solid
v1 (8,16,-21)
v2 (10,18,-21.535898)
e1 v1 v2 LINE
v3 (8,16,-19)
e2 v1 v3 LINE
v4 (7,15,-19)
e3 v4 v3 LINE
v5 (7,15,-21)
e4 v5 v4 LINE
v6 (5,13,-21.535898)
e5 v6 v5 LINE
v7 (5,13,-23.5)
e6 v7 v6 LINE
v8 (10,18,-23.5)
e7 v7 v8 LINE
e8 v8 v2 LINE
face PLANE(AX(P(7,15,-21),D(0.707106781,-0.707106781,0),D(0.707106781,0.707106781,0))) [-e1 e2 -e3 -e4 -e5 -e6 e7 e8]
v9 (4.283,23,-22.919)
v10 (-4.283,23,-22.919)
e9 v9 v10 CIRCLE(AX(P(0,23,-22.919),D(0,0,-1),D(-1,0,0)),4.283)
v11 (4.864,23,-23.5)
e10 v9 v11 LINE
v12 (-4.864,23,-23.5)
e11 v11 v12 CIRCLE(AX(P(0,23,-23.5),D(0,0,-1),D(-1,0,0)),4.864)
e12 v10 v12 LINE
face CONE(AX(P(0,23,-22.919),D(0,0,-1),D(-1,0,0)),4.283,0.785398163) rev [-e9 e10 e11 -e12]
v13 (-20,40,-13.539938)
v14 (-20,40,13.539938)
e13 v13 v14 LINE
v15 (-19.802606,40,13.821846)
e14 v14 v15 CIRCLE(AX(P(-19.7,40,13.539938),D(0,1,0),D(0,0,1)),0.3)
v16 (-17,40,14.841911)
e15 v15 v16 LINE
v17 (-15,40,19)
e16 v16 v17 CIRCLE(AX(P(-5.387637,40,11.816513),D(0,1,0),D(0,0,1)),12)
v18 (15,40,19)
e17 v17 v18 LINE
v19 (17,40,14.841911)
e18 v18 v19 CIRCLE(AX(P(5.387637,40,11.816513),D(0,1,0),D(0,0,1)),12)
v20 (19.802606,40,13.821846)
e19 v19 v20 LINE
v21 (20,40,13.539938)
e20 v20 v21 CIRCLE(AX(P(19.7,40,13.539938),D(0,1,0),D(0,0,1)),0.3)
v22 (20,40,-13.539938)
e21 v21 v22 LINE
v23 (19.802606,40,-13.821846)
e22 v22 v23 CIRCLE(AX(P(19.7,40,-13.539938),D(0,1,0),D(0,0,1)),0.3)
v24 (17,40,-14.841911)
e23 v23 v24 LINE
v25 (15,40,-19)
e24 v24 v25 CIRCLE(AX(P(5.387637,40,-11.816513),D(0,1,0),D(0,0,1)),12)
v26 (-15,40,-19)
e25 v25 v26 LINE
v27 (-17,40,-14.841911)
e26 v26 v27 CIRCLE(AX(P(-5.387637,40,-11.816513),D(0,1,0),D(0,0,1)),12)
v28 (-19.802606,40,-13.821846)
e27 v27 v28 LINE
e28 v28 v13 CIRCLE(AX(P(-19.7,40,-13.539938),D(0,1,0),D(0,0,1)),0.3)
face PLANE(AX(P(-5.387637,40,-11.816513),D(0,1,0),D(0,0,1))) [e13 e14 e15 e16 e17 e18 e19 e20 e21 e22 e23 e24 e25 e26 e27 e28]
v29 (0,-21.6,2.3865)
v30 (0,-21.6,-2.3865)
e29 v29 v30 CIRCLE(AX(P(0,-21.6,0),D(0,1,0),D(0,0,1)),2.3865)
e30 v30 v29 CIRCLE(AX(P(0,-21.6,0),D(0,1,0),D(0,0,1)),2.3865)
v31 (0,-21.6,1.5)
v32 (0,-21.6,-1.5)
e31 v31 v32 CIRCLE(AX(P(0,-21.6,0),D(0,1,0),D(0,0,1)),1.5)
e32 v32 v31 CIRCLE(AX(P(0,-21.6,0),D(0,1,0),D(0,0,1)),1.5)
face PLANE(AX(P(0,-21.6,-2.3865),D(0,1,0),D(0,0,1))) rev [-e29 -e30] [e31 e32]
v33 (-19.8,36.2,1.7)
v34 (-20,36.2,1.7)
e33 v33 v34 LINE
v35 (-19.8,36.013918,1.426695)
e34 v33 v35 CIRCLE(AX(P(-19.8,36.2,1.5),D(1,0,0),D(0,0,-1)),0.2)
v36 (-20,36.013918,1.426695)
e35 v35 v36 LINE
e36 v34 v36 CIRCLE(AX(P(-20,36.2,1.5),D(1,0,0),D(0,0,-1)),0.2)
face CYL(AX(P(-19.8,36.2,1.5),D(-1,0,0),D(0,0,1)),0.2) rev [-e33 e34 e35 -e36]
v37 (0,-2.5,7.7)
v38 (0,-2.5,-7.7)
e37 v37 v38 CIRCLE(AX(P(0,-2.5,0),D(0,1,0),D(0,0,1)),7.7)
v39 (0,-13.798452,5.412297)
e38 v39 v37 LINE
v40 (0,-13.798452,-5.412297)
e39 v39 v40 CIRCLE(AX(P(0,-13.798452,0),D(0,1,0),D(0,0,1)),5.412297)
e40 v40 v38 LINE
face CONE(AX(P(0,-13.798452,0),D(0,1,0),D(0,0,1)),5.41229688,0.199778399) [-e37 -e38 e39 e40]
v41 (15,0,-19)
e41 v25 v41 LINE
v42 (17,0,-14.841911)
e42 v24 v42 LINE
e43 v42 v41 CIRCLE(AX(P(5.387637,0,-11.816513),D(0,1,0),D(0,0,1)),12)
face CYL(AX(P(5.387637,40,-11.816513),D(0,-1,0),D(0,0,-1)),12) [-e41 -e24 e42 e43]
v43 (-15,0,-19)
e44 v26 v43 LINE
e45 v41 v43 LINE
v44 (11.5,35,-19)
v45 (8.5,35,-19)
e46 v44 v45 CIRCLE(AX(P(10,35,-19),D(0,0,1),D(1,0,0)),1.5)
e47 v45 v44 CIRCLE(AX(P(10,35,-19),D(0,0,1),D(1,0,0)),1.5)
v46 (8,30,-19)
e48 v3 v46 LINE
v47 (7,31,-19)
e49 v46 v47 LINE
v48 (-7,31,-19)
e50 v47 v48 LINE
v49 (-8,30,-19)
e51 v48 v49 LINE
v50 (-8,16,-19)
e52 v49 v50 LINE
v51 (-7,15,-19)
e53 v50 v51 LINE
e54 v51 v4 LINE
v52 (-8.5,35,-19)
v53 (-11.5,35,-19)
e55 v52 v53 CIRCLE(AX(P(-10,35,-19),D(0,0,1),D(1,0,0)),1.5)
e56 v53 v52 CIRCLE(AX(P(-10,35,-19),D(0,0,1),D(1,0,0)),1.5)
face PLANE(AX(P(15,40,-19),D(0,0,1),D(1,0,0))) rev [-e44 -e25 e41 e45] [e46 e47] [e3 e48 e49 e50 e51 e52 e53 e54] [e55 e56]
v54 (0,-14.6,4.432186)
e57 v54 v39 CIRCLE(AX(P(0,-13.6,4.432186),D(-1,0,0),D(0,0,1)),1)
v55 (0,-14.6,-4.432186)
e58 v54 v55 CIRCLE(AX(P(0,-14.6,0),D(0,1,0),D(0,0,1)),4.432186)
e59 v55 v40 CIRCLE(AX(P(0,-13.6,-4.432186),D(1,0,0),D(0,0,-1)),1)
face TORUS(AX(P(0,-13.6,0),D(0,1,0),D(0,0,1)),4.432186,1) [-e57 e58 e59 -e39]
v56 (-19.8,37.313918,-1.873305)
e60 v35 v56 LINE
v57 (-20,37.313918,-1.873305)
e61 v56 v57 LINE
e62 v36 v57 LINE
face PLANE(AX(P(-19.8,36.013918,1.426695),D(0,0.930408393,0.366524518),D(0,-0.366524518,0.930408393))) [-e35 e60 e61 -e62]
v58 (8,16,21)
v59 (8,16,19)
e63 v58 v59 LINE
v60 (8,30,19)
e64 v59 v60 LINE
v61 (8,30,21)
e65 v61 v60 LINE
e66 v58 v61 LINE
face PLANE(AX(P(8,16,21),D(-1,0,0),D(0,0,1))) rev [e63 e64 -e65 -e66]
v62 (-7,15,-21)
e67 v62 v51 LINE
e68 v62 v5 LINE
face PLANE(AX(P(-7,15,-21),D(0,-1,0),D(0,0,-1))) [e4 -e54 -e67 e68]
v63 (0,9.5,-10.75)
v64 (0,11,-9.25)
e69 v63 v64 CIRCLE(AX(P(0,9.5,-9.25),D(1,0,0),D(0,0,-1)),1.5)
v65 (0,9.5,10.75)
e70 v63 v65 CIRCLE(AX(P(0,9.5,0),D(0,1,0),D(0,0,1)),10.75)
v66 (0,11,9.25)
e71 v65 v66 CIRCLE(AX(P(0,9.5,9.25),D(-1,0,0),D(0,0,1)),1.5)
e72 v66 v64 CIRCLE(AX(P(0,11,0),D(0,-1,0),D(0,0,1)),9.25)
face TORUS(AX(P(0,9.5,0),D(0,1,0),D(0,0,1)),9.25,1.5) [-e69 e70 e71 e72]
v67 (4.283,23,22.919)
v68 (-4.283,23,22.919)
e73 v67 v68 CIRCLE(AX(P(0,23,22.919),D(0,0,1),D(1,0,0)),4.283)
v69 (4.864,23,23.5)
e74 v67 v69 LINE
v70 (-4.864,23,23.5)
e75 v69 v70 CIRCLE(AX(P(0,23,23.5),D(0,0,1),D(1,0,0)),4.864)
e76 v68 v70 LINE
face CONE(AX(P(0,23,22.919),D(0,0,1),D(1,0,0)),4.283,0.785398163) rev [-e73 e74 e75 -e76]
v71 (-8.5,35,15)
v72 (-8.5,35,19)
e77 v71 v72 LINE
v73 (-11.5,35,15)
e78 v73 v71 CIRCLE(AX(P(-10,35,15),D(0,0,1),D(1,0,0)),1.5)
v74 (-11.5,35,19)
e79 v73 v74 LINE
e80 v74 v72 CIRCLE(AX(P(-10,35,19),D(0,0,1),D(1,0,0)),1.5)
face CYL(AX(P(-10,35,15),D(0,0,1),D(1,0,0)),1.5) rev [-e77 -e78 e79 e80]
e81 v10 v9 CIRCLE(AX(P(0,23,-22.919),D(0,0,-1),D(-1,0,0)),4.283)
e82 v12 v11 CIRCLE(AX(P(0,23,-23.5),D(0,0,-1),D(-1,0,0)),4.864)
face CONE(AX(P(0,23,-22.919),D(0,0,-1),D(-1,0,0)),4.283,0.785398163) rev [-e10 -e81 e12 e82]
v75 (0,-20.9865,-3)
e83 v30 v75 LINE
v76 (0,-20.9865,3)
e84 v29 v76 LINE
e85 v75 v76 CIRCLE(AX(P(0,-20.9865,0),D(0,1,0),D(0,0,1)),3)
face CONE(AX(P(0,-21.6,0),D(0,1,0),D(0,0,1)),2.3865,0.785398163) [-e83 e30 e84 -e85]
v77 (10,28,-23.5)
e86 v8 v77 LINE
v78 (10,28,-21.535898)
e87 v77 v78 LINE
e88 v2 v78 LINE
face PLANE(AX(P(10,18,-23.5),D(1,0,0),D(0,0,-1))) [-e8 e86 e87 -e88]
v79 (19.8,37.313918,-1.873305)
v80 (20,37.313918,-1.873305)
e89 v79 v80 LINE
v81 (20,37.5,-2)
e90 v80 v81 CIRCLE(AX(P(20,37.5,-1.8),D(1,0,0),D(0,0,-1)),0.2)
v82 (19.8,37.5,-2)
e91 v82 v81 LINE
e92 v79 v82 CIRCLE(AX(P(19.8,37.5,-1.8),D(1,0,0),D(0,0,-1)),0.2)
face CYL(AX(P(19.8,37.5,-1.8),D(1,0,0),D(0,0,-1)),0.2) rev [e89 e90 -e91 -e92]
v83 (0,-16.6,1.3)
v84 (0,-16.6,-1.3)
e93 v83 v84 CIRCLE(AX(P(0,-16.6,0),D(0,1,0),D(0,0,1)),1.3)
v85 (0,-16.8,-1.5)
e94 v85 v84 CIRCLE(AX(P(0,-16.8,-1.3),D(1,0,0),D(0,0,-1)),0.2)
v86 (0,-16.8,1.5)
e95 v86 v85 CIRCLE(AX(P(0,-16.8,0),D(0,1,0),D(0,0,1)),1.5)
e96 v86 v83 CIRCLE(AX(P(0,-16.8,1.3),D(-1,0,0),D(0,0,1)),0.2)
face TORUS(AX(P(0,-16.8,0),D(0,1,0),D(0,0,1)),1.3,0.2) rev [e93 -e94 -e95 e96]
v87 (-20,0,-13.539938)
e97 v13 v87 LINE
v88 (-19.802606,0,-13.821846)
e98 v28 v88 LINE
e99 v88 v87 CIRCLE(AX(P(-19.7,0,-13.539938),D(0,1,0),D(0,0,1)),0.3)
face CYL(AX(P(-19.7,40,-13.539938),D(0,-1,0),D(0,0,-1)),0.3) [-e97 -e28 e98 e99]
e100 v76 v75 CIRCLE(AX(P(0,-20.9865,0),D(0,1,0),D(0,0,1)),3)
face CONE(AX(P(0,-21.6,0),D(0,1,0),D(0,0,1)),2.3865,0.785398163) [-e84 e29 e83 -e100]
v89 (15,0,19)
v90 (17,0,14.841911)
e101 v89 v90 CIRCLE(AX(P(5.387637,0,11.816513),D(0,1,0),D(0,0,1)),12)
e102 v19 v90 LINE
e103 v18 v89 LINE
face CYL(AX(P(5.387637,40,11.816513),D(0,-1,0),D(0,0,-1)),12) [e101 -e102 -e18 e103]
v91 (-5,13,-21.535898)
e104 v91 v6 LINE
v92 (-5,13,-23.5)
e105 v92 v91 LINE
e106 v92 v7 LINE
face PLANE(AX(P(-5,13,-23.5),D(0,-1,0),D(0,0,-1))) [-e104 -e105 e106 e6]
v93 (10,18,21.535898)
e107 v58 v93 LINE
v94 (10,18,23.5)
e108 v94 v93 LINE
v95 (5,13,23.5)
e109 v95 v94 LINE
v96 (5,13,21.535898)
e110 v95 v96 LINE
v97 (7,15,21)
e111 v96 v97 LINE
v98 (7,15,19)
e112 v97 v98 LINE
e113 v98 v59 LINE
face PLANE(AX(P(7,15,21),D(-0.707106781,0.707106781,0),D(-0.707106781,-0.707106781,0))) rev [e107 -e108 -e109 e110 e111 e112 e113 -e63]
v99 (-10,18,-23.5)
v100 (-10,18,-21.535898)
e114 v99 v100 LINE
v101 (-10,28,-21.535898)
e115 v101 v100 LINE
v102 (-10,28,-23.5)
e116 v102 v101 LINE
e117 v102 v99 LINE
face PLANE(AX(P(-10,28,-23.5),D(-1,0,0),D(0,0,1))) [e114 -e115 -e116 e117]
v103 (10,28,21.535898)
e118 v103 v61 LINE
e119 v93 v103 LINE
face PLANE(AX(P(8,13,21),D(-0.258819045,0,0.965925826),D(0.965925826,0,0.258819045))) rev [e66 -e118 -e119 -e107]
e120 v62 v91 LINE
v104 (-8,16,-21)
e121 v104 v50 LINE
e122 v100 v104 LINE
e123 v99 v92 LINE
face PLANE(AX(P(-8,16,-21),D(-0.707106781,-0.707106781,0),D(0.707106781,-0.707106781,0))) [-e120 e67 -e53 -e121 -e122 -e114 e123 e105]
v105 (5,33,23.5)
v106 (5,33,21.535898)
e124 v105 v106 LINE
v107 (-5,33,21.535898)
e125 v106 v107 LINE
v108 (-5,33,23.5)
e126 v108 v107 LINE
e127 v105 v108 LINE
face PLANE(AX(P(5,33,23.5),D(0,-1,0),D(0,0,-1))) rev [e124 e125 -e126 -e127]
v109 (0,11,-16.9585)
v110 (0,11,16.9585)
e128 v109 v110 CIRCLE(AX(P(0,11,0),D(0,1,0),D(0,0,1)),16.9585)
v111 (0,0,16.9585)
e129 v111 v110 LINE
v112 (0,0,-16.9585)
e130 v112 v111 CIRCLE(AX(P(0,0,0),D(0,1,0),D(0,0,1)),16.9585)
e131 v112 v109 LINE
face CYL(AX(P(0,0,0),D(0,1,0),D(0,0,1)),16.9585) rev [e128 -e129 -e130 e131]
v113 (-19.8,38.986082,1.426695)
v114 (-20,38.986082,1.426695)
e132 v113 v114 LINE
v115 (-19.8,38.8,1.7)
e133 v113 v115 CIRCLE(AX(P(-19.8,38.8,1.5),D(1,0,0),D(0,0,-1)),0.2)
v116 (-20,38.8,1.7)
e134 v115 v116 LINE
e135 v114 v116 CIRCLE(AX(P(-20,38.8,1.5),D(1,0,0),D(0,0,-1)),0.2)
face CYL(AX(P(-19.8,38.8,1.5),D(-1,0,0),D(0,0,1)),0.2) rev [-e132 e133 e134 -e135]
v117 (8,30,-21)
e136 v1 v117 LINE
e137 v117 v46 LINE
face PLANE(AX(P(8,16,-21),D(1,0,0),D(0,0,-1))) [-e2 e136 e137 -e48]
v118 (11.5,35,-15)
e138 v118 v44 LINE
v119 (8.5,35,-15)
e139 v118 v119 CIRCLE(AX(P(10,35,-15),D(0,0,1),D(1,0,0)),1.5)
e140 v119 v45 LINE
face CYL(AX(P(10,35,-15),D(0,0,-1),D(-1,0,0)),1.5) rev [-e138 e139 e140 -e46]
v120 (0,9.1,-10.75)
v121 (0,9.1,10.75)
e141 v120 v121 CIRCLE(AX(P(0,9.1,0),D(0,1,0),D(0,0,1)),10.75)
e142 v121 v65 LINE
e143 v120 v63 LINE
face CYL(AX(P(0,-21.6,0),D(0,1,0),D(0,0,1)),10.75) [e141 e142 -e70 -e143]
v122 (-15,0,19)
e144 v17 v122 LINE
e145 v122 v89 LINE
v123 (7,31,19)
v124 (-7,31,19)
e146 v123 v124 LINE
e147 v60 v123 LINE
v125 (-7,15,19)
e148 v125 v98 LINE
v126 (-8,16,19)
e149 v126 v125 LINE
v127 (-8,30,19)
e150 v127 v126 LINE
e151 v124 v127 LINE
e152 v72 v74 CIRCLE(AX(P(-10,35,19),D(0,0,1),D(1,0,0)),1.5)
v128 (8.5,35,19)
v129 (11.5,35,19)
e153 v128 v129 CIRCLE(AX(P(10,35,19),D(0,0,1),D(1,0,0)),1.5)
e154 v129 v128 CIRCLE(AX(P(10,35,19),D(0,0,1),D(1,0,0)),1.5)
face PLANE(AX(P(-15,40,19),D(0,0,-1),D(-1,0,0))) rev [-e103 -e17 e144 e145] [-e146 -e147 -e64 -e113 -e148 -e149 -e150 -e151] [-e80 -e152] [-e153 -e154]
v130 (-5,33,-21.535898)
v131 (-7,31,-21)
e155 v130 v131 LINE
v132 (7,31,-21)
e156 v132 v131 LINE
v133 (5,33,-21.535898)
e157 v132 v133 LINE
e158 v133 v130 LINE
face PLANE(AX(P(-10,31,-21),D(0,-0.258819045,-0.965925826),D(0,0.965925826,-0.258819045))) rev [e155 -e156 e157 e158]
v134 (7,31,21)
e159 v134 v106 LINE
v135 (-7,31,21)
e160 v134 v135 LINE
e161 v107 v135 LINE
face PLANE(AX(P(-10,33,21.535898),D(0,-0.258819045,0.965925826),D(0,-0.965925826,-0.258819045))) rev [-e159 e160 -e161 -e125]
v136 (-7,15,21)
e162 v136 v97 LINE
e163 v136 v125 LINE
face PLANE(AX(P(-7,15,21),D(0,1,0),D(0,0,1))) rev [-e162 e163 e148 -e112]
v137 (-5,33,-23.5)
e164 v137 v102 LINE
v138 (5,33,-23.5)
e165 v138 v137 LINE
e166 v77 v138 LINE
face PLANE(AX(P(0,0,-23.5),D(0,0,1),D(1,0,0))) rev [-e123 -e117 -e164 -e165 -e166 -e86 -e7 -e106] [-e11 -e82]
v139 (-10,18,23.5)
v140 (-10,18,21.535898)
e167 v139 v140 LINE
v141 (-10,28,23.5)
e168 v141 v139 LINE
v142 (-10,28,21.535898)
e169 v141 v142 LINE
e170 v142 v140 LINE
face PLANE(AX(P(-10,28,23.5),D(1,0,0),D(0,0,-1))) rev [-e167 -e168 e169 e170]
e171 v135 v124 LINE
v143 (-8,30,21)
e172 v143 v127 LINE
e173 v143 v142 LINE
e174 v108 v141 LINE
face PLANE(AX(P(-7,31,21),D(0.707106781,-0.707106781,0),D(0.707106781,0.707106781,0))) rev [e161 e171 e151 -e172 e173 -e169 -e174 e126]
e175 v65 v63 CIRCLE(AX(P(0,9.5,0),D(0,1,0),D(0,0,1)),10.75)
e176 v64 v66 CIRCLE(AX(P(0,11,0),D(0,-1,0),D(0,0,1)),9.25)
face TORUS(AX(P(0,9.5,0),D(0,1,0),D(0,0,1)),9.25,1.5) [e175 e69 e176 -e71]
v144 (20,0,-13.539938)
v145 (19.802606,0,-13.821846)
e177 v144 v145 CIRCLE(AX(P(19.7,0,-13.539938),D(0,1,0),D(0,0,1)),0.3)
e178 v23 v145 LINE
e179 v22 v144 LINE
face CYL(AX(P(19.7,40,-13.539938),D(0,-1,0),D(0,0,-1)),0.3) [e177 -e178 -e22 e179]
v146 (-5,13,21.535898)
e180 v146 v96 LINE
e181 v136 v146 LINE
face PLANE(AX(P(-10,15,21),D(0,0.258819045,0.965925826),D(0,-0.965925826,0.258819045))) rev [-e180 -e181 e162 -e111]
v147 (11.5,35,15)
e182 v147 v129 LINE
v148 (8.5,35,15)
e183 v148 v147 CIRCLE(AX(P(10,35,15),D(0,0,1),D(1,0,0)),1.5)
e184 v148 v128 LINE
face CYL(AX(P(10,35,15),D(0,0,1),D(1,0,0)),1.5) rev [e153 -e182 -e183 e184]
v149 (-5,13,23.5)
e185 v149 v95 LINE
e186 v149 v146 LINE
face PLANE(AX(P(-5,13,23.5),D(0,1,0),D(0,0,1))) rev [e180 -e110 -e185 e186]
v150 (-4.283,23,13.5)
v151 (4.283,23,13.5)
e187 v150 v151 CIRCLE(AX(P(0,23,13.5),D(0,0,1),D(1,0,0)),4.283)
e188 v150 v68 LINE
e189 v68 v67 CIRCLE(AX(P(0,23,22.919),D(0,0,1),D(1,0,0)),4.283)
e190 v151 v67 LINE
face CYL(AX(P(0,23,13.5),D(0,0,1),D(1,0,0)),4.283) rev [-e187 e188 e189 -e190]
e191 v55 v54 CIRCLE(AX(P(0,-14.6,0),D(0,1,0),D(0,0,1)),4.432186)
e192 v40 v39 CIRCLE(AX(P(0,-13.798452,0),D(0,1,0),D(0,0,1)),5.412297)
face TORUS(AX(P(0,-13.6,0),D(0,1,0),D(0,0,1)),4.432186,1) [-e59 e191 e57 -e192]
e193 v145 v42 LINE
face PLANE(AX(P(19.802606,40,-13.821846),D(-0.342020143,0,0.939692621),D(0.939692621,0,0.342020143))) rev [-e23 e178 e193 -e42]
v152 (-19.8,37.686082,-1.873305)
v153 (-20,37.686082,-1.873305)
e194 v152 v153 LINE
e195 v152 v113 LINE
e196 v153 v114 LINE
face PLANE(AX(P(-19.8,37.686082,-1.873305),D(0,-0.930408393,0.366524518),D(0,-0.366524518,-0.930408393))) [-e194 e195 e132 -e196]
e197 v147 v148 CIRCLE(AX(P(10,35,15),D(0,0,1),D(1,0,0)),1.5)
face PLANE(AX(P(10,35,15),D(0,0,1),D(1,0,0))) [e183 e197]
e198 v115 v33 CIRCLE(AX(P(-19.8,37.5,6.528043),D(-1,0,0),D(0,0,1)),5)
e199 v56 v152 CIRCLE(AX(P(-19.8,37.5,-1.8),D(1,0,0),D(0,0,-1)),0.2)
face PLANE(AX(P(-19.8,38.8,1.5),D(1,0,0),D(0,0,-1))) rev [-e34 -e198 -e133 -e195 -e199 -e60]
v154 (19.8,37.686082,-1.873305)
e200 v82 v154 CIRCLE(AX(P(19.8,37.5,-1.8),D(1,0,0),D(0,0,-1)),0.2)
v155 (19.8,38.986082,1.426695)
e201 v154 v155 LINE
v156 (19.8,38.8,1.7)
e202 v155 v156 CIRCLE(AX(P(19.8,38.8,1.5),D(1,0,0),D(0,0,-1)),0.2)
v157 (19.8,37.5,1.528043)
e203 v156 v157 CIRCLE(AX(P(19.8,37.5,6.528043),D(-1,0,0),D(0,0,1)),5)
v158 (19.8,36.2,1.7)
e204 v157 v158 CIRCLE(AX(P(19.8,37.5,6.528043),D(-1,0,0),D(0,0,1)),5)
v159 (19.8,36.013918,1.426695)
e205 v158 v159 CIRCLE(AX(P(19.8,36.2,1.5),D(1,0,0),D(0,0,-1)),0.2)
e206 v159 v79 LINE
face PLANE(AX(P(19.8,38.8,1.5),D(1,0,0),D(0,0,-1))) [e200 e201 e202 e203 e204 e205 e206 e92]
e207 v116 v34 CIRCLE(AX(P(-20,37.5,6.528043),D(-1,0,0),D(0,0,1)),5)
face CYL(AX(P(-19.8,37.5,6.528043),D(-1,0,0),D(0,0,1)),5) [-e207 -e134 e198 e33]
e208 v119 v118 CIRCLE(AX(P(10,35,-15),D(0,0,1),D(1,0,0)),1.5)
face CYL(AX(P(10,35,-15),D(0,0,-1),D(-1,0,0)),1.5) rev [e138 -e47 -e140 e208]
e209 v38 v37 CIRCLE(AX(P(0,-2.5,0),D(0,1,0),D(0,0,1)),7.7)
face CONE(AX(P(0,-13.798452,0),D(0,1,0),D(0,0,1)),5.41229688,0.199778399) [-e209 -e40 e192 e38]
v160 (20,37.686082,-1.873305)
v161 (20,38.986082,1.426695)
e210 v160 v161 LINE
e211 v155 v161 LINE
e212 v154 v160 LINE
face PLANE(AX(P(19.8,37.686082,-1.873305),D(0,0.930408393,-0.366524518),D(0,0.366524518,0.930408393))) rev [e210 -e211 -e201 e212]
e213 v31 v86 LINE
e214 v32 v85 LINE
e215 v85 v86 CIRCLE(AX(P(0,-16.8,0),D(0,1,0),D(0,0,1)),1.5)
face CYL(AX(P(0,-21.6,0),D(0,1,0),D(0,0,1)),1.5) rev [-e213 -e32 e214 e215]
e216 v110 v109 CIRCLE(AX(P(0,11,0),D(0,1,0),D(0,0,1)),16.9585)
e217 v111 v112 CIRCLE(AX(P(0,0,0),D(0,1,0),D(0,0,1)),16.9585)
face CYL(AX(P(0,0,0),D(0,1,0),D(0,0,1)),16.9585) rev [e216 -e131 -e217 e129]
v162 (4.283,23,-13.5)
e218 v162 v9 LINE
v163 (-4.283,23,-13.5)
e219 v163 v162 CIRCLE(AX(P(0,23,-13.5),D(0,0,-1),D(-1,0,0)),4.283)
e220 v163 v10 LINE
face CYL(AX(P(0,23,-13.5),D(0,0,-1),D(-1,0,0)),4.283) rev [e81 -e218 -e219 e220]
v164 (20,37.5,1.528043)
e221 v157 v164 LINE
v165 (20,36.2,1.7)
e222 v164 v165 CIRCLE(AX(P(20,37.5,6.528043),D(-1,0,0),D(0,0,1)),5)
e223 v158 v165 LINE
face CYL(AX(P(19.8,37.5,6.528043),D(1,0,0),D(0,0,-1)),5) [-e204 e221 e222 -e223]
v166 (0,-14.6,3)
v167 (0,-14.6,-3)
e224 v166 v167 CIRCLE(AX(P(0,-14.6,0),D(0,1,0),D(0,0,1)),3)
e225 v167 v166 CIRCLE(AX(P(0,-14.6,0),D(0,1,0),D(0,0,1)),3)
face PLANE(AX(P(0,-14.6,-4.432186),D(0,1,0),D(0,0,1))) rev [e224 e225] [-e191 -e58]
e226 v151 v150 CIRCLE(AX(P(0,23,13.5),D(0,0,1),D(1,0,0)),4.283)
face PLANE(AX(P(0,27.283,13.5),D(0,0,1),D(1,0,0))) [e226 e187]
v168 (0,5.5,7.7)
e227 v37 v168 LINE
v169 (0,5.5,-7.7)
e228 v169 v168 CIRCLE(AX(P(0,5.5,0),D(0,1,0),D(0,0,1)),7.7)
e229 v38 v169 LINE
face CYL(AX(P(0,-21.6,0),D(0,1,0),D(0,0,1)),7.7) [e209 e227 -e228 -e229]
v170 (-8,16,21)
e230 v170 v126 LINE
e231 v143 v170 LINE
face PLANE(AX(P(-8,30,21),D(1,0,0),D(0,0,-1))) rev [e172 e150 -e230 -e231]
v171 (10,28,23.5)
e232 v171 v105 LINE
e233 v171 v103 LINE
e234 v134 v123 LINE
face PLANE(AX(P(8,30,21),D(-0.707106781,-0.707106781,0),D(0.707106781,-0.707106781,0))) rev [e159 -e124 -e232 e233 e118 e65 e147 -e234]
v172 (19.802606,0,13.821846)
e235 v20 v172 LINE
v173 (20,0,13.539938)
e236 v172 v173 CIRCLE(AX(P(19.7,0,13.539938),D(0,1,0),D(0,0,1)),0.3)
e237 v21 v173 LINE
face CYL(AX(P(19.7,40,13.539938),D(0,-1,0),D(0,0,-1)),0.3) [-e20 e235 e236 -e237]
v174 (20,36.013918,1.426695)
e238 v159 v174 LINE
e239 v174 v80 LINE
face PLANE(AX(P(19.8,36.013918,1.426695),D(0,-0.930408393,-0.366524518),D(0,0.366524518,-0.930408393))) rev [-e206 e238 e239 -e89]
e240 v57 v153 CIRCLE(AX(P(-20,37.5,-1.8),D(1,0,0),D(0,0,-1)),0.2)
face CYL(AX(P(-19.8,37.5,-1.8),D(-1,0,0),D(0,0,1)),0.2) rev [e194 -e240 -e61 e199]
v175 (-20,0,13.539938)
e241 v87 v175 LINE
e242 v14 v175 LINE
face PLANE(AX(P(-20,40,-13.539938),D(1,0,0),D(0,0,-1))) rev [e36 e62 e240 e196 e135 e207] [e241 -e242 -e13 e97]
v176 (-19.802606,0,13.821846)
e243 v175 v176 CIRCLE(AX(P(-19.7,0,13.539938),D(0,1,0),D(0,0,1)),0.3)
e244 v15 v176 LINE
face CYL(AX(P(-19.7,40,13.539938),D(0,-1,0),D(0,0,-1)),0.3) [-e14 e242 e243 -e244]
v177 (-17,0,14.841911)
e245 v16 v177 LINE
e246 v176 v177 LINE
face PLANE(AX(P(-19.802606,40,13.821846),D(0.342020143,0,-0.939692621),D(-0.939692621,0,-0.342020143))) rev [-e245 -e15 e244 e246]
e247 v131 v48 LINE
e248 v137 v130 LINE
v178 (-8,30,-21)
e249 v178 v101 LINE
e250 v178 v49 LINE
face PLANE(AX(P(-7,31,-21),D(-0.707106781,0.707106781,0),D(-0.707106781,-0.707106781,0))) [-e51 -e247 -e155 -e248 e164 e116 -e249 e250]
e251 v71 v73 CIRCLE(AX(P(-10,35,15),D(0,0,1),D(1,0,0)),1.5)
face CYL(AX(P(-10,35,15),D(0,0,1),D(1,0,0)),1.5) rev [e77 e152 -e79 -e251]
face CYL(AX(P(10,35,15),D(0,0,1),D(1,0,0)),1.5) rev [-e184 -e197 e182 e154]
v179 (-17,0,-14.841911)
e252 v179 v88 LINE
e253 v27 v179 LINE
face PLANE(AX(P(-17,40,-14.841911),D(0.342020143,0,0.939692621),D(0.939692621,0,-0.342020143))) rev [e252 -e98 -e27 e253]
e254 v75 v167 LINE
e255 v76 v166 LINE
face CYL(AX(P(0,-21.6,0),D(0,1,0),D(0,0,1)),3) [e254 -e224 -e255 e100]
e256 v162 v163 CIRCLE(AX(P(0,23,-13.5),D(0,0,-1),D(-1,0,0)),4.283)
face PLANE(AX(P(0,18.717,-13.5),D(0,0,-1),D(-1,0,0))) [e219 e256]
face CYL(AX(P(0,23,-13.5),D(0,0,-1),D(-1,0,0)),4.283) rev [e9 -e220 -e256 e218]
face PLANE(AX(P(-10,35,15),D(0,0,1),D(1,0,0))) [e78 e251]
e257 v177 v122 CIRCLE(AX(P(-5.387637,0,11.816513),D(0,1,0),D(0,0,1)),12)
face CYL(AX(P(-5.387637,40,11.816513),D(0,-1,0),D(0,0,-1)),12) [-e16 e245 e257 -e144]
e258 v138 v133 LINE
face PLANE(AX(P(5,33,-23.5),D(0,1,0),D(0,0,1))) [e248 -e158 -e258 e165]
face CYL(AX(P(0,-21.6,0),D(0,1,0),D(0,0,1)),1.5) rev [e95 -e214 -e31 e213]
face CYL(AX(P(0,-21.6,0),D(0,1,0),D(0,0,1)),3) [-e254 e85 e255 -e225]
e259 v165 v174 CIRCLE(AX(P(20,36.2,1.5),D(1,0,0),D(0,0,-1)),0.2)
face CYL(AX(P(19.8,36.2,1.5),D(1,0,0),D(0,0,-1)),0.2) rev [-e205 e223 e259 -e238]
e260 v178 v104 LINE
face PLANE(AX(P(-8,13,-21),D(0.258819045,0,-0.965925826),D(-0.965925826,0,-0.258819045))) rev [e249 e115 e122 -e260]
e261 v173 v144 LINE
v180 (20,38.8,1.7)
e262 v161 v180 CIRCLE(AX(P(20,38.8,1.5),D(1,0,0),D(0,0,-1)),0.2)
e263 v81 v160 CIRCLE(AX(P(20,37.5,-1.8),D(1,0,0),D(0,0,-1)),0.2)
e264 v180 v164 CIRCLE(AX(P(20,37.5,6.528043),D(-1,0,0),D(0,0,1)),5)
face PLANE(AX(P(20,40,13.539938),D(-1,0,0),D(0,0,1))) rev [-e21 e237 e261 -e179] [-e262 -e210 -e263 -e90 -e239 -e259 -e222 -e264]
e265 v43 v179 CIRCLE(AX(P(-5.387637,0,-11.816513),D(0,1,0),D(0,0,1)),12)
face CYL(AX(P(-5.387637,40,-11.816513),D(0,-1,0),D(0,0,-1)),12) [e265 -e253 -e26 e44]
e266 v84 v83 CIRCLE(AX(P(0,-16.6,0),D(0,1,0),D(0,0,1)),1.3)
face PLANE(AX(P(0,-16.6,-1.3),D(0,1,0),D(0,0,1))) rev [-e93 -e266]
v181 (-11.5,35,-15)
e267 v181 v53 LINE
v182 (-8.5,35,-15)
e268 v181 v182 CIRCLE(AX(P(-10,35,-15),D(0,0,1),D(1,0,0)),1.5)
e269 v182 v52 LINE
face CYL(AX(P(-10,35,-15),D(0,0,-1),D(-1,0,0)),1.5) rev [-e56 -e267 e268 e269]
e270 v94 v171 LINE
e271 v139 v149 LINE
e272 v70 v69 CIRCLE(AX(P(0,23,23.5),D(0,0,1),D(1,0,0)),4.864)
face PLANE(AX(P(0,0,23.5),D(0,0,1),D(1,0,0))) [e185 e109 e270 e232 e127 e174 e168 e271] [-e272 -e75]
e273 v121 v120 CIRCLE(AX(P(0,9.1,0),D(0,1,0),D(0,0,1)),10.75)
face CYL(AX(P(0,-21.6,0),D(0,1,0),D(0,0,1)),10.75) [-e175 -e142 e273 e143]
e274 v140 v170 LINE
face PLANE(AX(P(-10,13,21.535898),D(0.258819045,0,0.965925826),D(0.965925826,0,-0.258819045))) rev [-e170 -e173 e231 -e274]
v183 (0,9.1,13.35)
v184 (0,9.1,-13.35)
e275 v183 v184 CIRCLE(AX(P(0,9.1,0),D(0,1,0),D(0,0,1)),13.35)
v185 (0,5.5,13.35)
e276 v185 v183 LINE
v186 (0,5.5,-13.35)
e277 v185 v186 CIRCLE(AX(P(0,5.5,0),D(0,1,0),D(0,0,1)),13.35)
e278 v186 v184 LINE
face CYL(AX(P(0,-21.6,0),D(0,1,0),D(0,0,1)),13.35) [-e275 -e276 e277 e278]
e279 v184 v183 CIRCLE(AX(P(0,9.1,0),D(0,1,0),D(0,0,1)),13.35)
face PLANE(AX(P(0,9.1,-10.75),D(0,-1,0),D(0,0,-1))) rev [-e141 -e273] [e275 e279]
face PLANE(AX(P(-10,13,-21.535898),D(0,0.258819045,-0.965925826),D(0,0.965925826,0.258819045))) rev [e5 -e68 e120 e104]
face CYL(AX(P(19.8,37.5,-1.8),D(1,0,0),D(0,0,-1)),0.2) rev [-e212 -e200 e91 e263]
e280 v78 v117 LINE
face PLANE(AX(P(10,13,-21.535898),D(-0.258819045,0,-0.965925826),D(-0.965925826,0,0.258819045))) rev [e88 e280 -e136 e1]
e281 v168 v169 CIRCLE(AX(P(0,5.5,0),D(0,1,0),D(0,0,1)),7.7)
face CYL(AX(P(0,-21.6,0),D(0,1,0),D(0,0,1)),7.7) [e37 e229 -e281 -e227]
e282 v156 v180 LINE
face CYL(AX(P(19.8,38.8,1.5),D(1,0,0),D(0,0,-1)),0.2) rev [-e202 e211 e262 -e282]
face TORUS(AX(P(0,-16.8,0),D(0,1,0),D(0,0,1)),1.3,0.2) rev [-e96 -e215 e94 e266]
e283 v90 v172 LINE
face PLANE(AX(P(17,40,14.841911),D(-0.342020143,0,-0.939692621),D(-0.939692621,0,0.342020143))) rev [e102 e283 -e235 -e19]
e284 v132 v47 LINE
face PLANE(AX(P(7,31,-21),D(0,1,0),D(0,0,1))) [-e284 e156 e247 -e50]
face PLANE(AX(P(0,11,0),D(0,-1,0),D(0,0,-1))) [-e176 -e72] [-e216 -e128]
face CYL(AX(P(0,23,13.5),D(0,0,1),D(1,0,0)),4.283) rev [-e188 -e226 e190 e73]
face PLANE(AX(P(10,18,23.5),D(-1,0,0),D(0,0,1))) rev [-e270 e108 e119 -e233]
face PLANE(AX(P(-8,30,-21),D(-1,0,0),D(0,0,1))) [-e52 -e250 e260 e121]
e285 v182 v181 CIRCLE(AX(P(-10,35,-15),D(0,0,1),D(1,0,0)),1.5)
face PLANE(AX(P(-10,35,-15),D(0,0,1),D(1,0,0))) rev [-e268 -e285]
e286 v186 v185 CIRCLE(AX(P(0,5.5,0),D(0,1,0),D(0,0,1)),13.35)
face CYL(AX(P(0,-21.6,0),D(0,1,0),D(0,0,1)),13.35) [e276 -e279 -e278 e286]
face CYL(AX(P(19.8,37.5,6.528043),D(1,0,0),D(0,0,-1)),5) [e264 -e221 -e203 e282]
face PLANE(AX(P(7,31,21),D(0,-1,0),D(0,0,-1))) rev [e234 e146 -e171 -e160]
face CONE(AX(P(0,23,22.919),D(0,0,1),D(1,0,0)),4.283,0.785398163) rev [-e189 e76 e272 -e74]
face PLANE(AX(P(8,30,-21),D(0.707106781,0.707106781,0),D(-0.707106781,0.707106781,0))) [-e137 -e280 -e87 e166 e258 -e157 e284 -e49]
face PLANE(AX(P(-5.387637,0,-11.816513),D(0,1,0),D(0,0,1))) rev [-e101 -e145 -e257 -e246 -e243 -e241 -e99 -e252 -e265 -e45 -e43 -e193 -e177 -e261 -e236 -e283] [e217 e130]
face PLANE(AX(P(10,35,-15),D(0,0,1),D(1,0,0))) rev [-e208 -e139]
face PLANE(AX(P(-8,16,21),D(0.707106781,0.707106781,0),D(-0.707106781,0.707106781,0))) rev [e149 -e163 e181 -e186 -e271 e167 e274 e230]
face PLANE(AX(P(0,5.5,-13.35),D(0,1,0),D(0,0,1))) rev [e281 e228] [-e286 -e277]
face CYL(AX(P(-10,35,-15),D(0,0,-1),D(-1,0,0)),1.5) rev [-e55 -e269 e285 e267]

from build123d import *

# Parameters (mm, degrees)
EXTRUDE_1_DEPTH          = 40
EXTRUDE_2_DEPTH          = 40
EXTRUDE_3_DEPTH          = 40
EXTRUDE_4_DEPTH          = 2
EXTRUDE_5_DEPTH          = 2.5
CUT_EXTRUDE_1_DEPTH      = 10
CUT_EXTRUDE_1_DEPTH_BACK = 10
CUT_EXTRUDE_2_DEPTH      = 10
CUT_EXTRUDE_2_DEPTH_BACK = 10
CUT_EXTRUDE_3_DEPTH      = 10
CUT_EXTRUDE_3_DEPTH_BACK = 10
CUT_EXTRUDE_4_DEPTH      = 10
CUT_EXTRUDE_4_DEPTH_BACK = 10
EXTRUDE_6_DEPTH          = 2
EXTRUDE_7_DEPTH          = 2.5
CUT_EXTRUDE_5_DEPTH      = 10
CUT_EXTRUDE_5_DEPTH_BACK = 10
CUT_EXTRUDE_6_DEPTH      = 10
CUT_EXTRUDE_6_DEPTH_BACK = 10
CUT_EXTRUDE_7_DEPTH      = 10
CUT_EXTRUDE_7_DEPTH_BACK = 10
CUT_EXTRUDE_8_DEPTH      = 10
CUT_EXTRUDE_8_DEPTH_BACK = 10
SKETCH_18_R              = 1.5
CUT_EXTRUDE_9_DEPTH      = 4
SKETCH_19_R              = 1.5
CUT_EXTRUDE_10_DEPTH     = 4
CUT_EXTRUDE_START        = -4
SKETCH_20_R              = 1.5
CUT_EXTRUDE_11_DEPTH     = 4
SKETCH_21_R              = 1.5
CUT_EXTRUDE_12_DEPTH     = 4
SKETCH_22_W              = 16.9585
SKETCH_22_H              = 11
CUT_EXTRUDE_13_DEPTH     = 0.2
CUT_EXTRUDE_START_2      = 0.2
CUT_EXTRUDE_14_DEPTH     = 0.2


with BuildPart() as part:
    # 草图1 → 凸台-拉伸1 (new body)
    with BuildSketch(Plane(origin=(0, 0, 0), x_dir=(1, 0, 0), z_dir=(0, 1, 0))):
        with BuildLine():
            Line((-17, 14.841910703), (-17, -14.841910703))
            ThreePointArc((-17, -14.841910703), (-16.201733132, -17.017987001), (-15, -19))
            Line((-15, -19), (15, -19))
            ThreePointArc((15, -19), (16.201733132, -17.017987001), (17, -14.841910703))
            Line((17, -14.841910703), (17, 14.841910703))
            ThreePointArc((17, 14.841910703), (16.201733132, 17.017987001), (15, 19))
            Line((15, 19), (-15, 19))
            ThreePointArc((-15, 19), (-16.201733132, 17.017987001), (-17, 14.841910703))
        make_face()
    extrude(amount=EXTRUDE_1_DEPTH)

    # 草图2 → 凸台-拉伸2 (add)
    with BuildSketch(Plane(origin=(0, 0, 0), x_dir=(1, 0, 0), z_dir=(0, 1, 0))):
        with BuildLine():
            Line((17, 14.841910703), (17, -14.841910703))
            Line((17, -14.841910703), (19.802606043, -13.821845525))
            ThreePointArc((19.802606043, -13.821845525), (19.945745613, -13.712010669), (20, -13.539937739))
            Line((20, -13.539937739), (20, 13.539937739))
            ThreePointArc((20, 13.539937739), (19.945745613, 13.712010669), (19.802606043, 13.821845525))
            Line((19.802606043, 13.821845525), (17, 14.841910703))
        make_face()
    extrude(amount=EXTRUDE_2_DEPTH)

    # 草图3 → 凸台-拉伸3 (add)
    with BuildSketch(Plane(origin=(0, 0, 0), x_dir=(1, 0, 0), z_dir=(0, 1, 0))):
        with BuildLine():
            Line((-19.802606043, -13.821845525), (-17, -14.841910703))
            Line((-17, -14.841910703), (-17, 14.841910703))
            Line((-17, 14.841910703), (-19.802606043, 13.821845525))
            ThreePointArc((-19.802606043, 13.821845525), (-19.945745613, 13.712010669), (-20, 13.539937739))
            Line((-20, 13.539937739), (-20, -13.539937739))
            ThreePointArc((-20, -13.539937739), (-19.945745613, -13.712010669), (-19.802606043, -13.821845525))
        make_face()
    extrude(amount=EXTRUDE_3_DEPTH)

    # 草图4 → 凸台-拉伸4 (add)
    with BuildSketch(Plane.XY.offset(-19)):
        Polygon((-8, 16), (-7, 15), (7, 15), (8, 16), (8, 30), (7, 31), (-7, 31), (-8, 30), align=None)
    extrude(amount=-EXTRUDE_4_DEPTH)

    # 草图5 → 凸台-拉伸5 (add)
    with BuildSketch(Plane.XY.offset(-21)):
        Polygon((-10, 18), (-5, 13), (5, 13), (10, 18), (10, 28), (5, 33), (-5, 33), (-10, 28), align=None)
    extrude(amount=-EXTRUDE_5_DEPTH)

    # 草图6 → 切除-拉伸1 (cut, two sides: drawn at the far end of the back side and taken through both)
    with BuildSketch(Plane(origin=(0, 0, 0), x_dir=(0, 0, -1), z_dir=(1, 0, 0)).offset(-CUT_EXTRUDE_1_DEPTH_BACK)):
        Polygon((21, 13), (21.535898385, 13), (21, 15), align=None)
    extrude(amount=CUT_EXTRUDE_1_DEPTH + CUT_EXTRUDE_1_DEPTH_BACK, mode=Mode.SUBTRACT)

    # 草图7 → 切除-拉伸2 (cut, two sides: drawn at the far end of the back side and taken through both)
    with BuildSketch(Plane(origin=(0, 0, 0), x_dir=(0, 0, -1), z_dir=(1, 0, 0)).offset(-CUT_EXTRUDE_2_DEPTH_BACK)):
        Polygon((21, 33), (21, 31), (21.535898385, 33), align=None)
    extrude(amount=CUT_EXTRUDE_2_DEPTH + CUT_EXTRUDE_2_DEPTH_BACK, mode=Mode.SUBTRACT)

    # 草图8 → 切除-拉伸3 (cut, two sides: drawn at the far end of the back side and taken through both)
    with BuildSketch(Plane(origin=(0, 23, 0), x_dir=(1, 0, 0), z_dir=(0, 1, 0)).offset(-CUT_EXTRUDE_3_DEPTH_BACK)):
        Polygon((8, 21), (10, 21), (10, 21.535898385), align=None)
    extrude(amount=CUT_EXTRUDE_3_DEPTH + CUT_EXTRUDE_3_DEPTH_BACK, mode=Mode.SUBTRACT)

    # 草图9 → 切除-拉伸4 (cut, two sides: drawn at the far end of the back side and taken through both)
    with BuildSketch(Plane(origin=(0, 23, 0), x_dir=(1, 0, 0), z_dir=(0, 1, 0)).offset(-CUT_EXTRUDE_4_DEPTH_BACK)):
        Polygon((-10, 21), (-8, 21), (-10, 21.535898385), align=None)
    extrude(amount=CUT_EXTRUDE_4_DEPTH + CUT_EXTRUDE_4_DEPTH_BACK, mode=Mode.SUBTRACT)

    # 草图10 → 凸台-拉伸6 (add)
    with BuildSketch(Plane.XY.offset(19)):
        Polygon((-8, 16), (-7, 15), (7, 15), (8, 16), (8, 30), (7, 31), (-7, 31), (-8, 30), align=None)
    extrude(amount=EXTRUDE_6_DEPTH)

    # 草图11 → 凸台-拉伸7 (add)
    with BuildSketch(Plane.XY.offset(21)):
        Polygon((-10, 18), (-5, 13), (5, 13), (10, 18), (10, 28), (5, 33), (-5, 33), (-10, 28), align=None)
    extrude(amount=EXTRUDE_7_DEPTH)

    # 草图12 → 切除-拉伸5 (cut, two sides: drawn at the far end of the back side and taken through both)
    with BuildSketch(Plane(origin=(0, 0, 0), x_dir=(0, 0, -1), z_dir=(1, 0, 0)).offset(-CUT_EXTRUDE_5_DEPTH_BACK)):
        Polygon((-21.535898385, 13), (-21, 13), (-21, 15), align=None)
    extrude(amount=CUT_EXTRUDE_5_DEPTH + CUT_EXTRUDE_5_DEPTH_BACK, mode=Mode.SUBTRACT)

    # 草图13 → 切除-拉伸6 (cut, two sides: drawn at the far end of the back side and taken through both)
    with BuildSketch(Plane(origin=(0, 0, 0), x_dir=(0, 0, -1), z_dir=(1, 0, 0)).offset(-CUT_EXTRUDE_6_DEPTH_BACK)):
        Polygon((-21.535898385, 33), (-21, 31), (-21, 33), align=None)
    extrude(amount=CUT_EXTRUDE_6_DEPTH + CUT_EXTRUDE_6_DEPTH_BACK, mode=Mode.SUBTRACT)

    # 草图14 → 切除-拉伸7 (cut, two sides: drawn at the far end of the back side and taken through both)
    with BuildSketch(Plane(origin=(0, 23, 0), x_dir=(1, 0, 0), z_dir=(0, 1, 0)).offset(-CUT_EXTRUDE_7_DEPTH_BACK)):
        Polygon((8, -21), (10, -21.535898385), (10, -21), align=None)
    extrude(amount=CUT_EXTRUDE_7_DEPTH + CUT_EXTRUDE_7_DEPTH_BACK, mode=Mode.SUBTRACT)

    # 草图15 → 切除-拉伸8 (cut, two sides: drawn at the far end of the back side and taken through both)
    with BuildSketch(Plane(origin=(0, 23, 0), x_dir=(1, 0, 0), z_dir=(0, 1, 0)).offset(-CUT_EXTRUDE_8_DEPTH_BACK)):
        Polygon((-10, -21), (-10, -21.535898385), (-8, -21), align=None)
    extrude(amount=CUT_EXTRUDE_8_DEPTH + CUT_EXTRUDE_8_DEPTH_BACK, mode=Mode.SUBTRACT)

    # 草图16 → 切除-旋转1 (revolve, cut)
    with BuildSketch(Plane(origin=(0, 0, 0), x_dir=(0, 0, -1), z_dir=(1, 0, 0)), mode=Mode.PRIVATE) as cut_revolve_1_sk:
        Polygon((23.5, 23), (23.5, 18.136), (22.919, 18.717), (13.5, 18.717), (13.5, 23), align=None)
    revolve(cut_revolve_1_sk.sketch.rotate(Axis((0, 23, -13.5), (0, 0, -1)), 90), axis=Axis((0, 23, -13.5), (0, 0, -1)), mode=Mode.SUBTRACT)

    # 草图17 → 切除-旋转2 (revolve, cut)
    with BuildSketch(Plane(origin=(0, 0, 0), x_dir=(0, 0, -1), z_dir=(1, 0, 0)), mode=Mode.PRIVATE) as cut_revolve_2_sk:
        Polygon((-23.5, 23), (-23.5, 27.864), (-22.919, 27.283), (-13.5, 27.283), (-13.5, 23), align=None)
    revolve(cut_revolve_2_sk.sketch.rotate(Axis((0, 23, 13.5), (0, 0, 1)), 270), axis=Axis((0, 23, 13.5), (0, 0, 1)), mode=Mode.SUBTRACT)

    # 草图18 → 切除-拉伸9 (cut)
    with BuildSketch(Plane.XY.offset(-19)):
        with Locations((-10, 35)):
            Circle(SKETCH_18_R)
    extrude(amount=CUT_EXTRUDE_9_DEPTH, mode=Mode.SUBTRACT)

    # 草图19 → 切除-拉伸10 (cut)
    with BuildSketch(Plane.XY.offset(-19)):
        with Locations((10, 35)):
            Circle(SKETCH_19_R)
    extrude(amount=CUT_EXTRUDE_10_DEPTH, mode=Mode.SUBTRACT)

    # 草图20 → 切除-拉伸11 (cut)
    with BuildSketch(Plane.XY.offset(19).offset(CUT_EXTRUDE_START)):
        with Locations((-10, 35)):
            Circle(SKETCH_20_R)
    extrude(amount=CUT_EXTRUDE_11_DEPTH, mode=Mode.SUBTRACT)

    # 草图21 → 切除-拉伸12 (cut)
    with BuildSketch(Plane.XY.offset(19).offset(CUT_EXTRUDE_START)):
        with Locations((10, 35)):
            Circle(SKETCH_21_R)
    extrude(amount=CUT_EXTRUDE_12_DEPTH, mode=Mode.SUBTRACT)

    # 草图22 → 切除-旋转3 (revolve, cut)
    with BuildSketch(Plane(origin=(0, 0, 0), x_dir=(0, 0, -1), z_dir=(1, 0, 0)), mode=Mode.PRIVATE) as cut_revolve_3_sk:
        with Locations((8.47925, 5.5)):
            Rectangle(SKETCH_22_W, SKETCH_22_H)
    revolve(cut_revolve_3_sk.sketch.rotate(Axis((0, 0, 0), (0, 1, 0)), 180), axis=Axis((0, 0, 0), (0, 1, 0)), mode=Mode.SUBTRACT)

    # 草图23 → 旋转1 (revolve)
    with BuildSketch(Plane(origin=(0, 0, 0), x_dir=(0, 0, -1), z_dir=(1, 0, 0)), mode=Mode.PRIVATE) as revolve_1_sk:
        with BuildLine():
            Line((0, 11), (9.25, 11))
            ThreePointArc((9.25, 11), (10.310660172, 10.560660172), (10.75, 9.5))
            Line((10.75, 9.5), (10.75, 9.1))
            Line((10.75, 9.1), (13.35, 9.1))
            Line((13.35, 9.1), (13.35, 5.5))
            Line((13.35, 5.5), (7.7, 5.5))
            Line((7.7, 5.5), (7.7, -2.5))
            Line((7.7, -2.5), (5.41229688, -13.798452142))
            ThreePointArc((5.41229688, -13.798452142), (5.065253382, -14.374096939), (4.432186301, -14.6))
            Line((4.432186301, -14.6), (3, -14.6))
            Line((3, -14.6), (3, -20.9865))
            Line((3, -20.9865), (2.3865, -21.6))
            Line((2.3865, -21.6), (1.5, -21.6))
            Line((1.5, -21.6), (1.5, -16.8))
            ThreePointArc((1.5, -16.8), (1.441421356, -16.658578644), (1.3, -16.6))
            Line((1.3, -16.6), (0, -16.6))
            Line((0, -16.6), (0, 11))
        make_face()
    revolve(revolve_1_sk.sketch.rotate(Axis((0, -21.6, 0), (0, 1, 0)), 180), axis=Axis((0, -21.6, 0), (0, 1, 0)))

    # 草图24 → 切除-拉伸13 (cut)
    with BuildSketch(Plane(origin=(20, 0, 0), x_dir=(0, 0, -1), z_dir=(1, 0, 0))):
        with BuildLine():
            Line((-1.426695096, 36.013918321), (1.873304904, 37.313918321))
            ThreePointArc((1.873304904, 37.313918321), (2, 37.5), (1.873304904, 37.686081679))
            Line((1.873304904, 37.686081679), (-1.426695096, 38.986081679))
            ThreePointArc((-1.426695096, 38.986081679), (-1.612558916, 38.965319359), (-1.7, 38.8))
            ThreePointArc((-1.7, 38.8), (-1.528043082, 37.5), (-1.7, 36.2))
            ThreePointArc((-1.7, 36.2), (-1.612558916, 36.034680641), (-1.426695096, 36.013918321))
        make_face()
    extrude(amount=-CUT_EXTRUDE_13_DEPTH, mode=Mode.SUBTRACT)

    # 草图25 → 切除-拉伸14 (cut)
    with BuildSketch(Plane(origin=(-20, 0, 0), x_dir=(0, 0, -1), z_dir=(1, 0, 0)).offset(CUT_EXTRUDE_START_2)):
        with BuildLine():
            Line((-1.426695096, 36.013918321), (1.873304904, 37.313918321))
            ThreePointArc((1.873304904, 37.313918321), (2, 37.5), (1.873304904, 37.686081679))
            Line((1.873304904, 37.686081679), (-1.426695096, 38.986081679))
            ThreePointArc((-1.426695096, 38.986081679), (-1.612558916, 38.965319359), (-1.7, 38.8))
            ThreePointArc((-1.7, 38.8), (-1.528043082, 37.5), (-1.7, 36.2))
            ThreePointArc((-1.7, 36.2), (-1.612558916, 36.034680641), (-1.426695096, 36.013918321))
        make_face()
    extrude(amount=-CUT_EXTRUDE_14_DEPTH, mode=Mode.SUBTRACT)


solid = part.part
